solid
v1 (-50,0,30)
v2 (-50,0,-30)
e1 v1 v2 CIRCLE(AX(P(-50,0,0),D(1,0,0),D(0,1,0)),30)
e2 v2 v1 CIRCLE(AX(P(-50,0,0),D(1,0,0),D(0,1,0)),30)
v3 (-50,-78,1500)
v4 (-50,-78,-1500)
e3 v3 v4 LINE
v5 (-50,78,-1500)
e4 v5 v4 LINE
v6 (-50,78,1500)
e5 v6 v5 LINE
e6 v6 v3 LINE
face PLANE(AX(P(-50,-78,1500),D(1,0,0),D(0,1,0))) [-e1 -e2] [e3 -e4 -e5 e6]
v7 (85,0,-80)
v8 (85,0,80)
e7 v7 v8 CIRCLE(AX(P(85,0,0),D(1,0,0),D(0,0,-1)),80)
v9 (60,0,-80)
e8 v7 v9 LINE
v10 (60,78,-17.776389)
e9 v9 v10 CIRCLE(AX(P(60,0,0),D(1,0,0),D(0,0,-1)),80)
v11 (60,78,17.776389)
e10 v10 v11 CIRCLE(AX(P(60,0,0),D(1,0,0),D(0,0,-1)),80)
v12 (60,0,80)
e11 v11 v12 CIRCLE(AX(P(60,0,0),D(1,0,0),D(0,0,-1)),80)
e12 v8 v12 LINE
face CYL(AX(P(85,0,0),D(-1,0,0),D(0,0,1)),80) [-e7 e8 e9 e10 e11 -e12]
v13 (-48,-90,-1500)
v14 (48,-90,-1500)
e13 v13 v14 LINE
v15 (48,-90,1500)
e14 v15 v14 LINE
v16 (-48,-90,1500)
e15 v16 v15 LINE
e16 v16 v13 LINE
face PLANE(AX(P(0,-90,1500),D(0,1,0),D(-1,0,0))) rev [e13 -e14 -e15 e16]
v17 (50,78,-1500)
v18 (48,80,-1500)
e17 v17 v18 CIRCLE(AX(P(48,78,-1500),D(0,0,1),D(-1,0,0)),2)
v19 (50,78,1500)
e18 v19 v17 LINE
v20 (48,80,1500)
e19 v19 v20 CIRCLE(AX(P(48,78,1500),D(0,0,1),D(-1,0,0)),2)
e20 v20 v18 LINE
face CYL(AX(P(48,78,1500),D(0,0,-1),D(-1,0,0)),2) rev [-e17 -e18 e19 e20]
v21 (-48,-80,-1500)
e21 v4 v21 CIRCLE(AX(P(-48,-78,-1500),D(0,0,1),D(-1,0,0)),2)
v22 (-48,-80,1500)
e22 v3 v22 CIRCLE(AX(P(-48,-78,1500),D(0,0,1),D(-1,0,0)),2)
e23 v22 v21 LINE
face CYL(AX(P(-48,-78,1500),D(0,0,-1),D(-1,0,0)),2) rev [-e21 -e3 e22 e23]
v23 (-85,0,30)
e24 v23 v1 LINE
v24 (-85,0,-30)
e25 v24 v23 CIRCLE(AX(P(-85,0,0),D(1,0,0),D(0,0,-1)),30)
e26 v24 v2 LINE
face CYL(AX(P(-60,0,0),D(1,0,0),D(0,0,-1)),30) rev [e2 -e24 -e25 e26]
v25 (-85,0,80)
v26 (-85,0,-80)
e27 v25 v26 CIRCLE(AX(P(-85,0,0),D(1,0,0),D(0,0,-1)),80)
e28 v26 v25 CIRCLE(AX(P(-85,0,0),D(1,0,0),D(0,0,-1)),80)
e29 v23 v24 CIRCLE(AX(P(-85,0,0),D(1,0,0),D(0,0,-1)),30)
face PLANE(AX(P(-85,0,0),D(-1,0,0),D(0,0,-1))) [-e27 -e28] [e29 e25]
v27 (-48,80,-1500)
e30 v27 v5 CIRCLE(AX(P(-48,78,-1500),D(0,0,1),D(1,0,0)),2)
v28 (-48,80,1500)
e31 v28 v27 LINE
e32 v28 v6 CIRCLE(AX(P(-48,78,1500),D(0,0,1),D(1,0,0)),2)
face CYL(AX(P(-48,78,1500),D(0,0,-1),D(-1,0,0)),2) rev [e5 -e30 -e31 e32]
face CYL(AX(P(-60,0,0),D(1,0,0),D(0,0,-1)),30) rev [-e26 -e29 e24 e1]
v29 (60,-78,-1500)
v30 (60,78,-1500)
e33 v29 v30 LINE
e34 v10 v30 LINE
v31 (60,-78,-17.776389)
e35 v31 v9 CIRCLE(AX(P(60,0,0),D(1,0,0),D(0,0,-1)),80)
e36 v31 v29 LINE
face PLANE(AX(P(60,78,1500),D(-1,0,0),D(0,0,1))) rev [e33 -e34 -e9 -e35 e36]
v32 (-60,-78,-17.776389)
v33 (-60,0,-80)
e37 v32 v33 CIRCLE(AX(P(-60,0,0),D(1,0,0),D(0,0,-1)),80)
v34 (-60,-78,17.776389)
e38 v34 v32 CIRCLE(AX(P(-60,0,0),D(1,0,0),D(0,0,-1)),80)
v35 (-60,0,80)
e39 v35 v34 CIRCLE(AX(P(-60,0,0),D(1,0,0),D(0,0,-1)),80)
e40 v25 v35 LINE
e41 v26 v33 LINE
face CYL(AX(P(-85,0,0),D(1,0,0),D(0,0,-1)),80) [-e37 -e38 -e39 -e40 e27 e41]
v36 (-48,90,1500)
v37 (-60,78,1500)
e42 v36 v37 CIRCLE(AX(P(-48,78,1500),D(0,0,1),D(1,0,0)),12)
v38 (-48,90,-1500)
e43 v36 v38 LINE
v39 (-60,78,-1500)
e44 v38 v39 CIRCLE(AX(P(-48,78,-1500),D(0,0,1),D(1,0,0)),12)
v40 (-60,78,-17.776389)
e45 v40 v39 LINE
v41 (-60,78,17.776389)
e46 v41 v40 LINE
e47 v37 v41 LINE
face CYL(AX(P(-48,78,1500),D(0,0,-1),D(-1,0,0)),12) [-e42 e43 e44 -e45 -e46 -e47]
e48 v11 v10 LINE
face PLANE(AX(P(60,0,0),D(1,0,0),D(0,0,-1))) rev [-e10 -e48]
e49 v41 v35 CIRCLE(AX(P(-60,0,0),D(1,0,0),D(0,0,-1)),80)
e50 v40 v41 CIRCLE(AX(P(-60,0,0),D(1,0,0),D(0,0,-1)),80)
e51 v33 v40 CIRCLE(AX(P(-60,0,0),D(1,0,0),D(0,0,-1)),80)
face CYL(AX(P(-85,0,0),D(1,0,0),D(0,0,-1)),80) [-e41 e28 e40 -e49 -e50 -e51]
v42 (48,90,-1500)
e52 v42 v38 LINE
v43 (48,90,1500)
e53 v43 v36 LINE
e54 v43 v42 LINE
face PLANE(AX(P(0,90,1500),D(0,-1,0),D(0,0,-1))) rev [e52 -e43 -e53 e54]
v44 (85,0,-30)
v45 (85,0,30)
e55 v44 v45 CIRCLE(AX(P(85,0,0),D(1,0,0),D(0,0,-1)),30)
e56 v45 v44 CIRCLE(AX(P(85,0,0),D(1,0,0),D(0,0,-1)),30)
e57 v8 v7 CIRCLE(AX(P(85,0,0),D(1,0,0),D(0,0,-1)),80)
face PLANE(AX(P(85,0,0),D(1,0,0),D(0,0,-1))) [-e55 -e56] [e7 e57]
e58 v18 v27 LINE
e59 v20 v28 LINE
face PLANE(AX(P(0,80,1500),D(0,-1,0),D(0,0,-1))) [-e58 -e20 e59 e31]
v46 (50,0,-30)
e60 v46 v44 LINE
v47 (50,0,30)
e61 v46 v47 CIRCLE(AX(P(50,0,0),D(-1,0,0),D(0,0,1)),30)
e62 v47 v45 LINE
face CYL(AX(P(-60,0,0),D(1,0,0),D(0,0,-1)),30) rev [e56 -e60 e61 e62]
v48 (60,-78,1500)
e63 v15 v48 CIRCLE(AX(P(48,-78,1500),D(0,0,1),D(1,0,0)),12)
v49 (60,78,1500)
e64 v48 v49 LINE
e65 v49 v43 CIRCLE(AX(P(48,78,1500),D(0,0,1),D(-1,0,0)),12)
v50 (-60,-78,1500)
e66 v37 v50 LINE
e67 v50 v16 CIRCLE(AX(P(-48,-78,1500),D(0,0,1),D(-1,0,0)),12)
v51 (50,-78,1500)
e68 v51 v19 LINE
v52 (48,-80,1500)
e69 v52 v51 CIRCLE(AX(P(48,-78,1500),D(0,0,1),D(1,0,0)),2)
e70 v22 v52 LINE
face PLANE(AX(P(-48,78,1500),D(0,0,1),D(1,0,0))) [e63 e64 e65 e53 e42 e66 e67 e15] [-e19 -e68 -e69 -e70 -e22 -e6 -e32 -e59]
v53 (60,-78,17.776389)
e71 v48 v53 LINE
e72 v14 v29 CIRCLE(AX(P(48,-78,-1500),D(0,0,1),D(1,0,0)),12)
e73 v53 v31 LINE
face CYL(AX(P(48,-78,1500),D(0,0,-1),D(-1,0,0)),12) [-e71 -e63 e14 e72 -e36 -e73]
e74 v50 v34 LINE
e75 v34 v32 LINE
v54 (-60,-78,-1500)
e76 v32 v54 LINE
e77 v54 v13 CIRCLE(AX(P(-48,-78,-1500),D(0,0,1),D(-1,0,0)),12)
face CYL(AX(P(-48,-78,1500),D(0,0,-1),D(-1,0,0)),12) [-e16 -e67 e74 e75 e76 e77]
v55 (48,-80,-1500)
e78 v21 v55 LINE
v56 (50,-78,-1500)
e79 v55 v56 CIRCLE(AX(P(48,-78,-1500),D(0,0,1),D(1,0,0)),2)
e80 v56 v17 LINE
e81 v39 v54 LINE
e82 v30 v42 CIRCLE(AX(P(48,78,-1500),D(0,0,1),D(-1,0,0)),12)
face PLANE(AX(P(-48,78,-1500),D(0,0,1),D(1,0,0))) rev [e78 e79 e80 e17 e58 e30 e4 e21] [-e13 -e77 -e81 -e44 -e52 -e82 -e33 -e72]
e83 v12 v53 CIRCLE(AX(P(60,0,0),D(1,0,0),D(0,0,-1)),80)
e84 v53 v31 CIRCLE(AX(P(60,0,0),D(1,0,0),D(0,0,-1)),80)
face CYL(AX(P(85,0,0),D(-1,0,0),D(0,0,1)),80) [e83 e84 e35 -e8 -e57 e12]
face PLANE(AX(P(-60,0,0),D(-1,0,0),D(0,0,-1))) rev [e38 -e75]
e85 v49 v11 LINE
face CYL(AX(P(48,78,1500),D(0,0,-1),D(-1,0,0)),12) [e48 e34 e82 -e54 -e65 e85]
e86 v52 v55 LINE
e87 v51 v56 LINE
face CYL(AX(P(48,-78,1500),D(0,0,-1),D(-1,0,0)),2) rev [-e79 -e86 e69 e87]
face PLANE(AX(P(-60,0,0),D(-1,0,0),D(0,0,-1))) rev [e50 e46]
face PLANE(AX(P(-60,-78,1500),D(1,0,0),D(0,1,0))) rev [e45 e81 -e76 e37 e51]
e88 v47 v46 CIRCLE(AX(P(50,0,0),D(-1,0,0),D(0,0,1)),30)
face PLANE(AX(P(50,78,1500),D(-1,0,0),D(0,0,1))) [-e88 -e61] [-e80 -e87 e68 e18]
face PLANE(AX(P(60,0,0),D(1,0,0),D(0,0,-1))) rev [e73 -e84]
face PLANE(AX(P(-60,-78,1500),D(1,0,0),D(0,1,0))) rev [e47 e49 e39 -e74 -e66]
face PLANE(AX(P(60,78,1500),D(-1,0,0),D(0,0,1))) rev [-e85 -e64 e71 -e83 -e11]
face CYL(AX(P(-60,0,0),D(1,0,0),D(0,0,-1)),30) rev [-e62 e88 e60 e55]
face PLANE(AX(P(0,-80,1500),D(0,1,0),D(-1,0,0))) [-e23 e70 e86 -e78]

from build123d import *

# Parameters (mm, degrees)
BOSS_EXTRUDE_1_DEPTH     = 1500
CUT_EXTRUDE_1_DEPTH      = 1504.894943139
CUT_EXTRUDE_1_DEPTH_BACK = 1504.894943139
SKETCH_2_R               = 30
SKETCH_3_R               = 80
SKETCH_3_R_2             = 30
BOSS_EXTRUDE_2_DEPTH     = 25


with BuildPart() as part:
    # Sketch 1 → Boss-Extrude 1 (new, symmetric)
    with BuildSketch(Plane.XY):
        with BuildLine():
            Line((0, 90), (-48, 90))
            ThreePointArc((-48, 90), (-56.485281374, 86.485281374), (-60, 78))
            Line((-60, 78), (-60, 0))
            Line((-60, 0), (-60, -78))
            ThreePointArc((-60, -78), (-56.485281374, -86.485281374), (-48, -90))
            Line((-48, -90), (0, -90))
            Line((0, -90), (48, -90))
            ThreePointArc((48, -90), (56.485281374, -86.485281374), (60, -78))
            Line((60, -78), (60, 78))
            ThreePointArc((60, 78), (56.485281374, 86.485281374), (48, 90))
            Line((48, 90), (0, 90))
        make_face()
        with BuildLine():
            Line((0, 80), (-48, 80))
            ThreePointArc((-48, 80), (-49.414213562, 79.414213562), (-50, 78))
            Line((-50, 78), (-50, 0))
            Line((-50, 0), (-50, -78))
            ThreePointArc((-50, -78), (-49.414213562, -79.414213562), (-48, -80))
            Line((-48, -80), (0, -80))
            Line((0, -80), (48, -80))
            ThreePointArc((48, -80), (49.414213562, -79.414213562), (50, -78))
            Line((50, -78), (50, 78))
            ThreePointArc((50, 78), (49.414213562, 79.414213562), (48, 80))
            Line((48, 80), (0, 80))
        make_face(mode=Mode.SUBTRACT)
    extrude(amount=BOSS_EXTRUDE_1_DEPTH, both=True)

    # Sketch 2 → Cut-Extrude 1 (cut, two sides: drawn at the far end of the back side and taken through both)
    with BuildSketch(Plane(origin=(0, 0, 0), x_dir=(0, 0, -1), z_dir=(1, 0, 0)).offset(-CUT_EXTRUDE_1_DEPTH_BACK)):
        Circle(SKETCH_2_R)
    extrude(amount=CUT_EXTRUDE_1_DEPTH + CUT_EXTRUDE_1_DEPTH_BACK, mode=Mode.SUBTRACT)

    # Sketch 3 → Boss-Extrude 2 (add)
    with BuildSketch(Plane(origin=(60, 0, 0), x_dir=(0, 0, -1), z_dir=(1, 0, 0))):
        with Locations(Location((0, 0, 0), (0, 0, 102.838568141))):
            Circle(SKETCH_3_R)
        Circle(SKETCH_3_R_2, mode=Mode.SUBTRACT)
    boss_extrude_2 = extrude(amount=BOSS_EXTRUDE_2_DEPTH)

    # Mirror 1: Boss-Extrude 2 across plane
    add(boss_extrude_2.mirror(Plane(origin=(0, 0, 0), x_dir=(0, 0, 1), z_dir=(1, 0, 0))))


solid = part.part
